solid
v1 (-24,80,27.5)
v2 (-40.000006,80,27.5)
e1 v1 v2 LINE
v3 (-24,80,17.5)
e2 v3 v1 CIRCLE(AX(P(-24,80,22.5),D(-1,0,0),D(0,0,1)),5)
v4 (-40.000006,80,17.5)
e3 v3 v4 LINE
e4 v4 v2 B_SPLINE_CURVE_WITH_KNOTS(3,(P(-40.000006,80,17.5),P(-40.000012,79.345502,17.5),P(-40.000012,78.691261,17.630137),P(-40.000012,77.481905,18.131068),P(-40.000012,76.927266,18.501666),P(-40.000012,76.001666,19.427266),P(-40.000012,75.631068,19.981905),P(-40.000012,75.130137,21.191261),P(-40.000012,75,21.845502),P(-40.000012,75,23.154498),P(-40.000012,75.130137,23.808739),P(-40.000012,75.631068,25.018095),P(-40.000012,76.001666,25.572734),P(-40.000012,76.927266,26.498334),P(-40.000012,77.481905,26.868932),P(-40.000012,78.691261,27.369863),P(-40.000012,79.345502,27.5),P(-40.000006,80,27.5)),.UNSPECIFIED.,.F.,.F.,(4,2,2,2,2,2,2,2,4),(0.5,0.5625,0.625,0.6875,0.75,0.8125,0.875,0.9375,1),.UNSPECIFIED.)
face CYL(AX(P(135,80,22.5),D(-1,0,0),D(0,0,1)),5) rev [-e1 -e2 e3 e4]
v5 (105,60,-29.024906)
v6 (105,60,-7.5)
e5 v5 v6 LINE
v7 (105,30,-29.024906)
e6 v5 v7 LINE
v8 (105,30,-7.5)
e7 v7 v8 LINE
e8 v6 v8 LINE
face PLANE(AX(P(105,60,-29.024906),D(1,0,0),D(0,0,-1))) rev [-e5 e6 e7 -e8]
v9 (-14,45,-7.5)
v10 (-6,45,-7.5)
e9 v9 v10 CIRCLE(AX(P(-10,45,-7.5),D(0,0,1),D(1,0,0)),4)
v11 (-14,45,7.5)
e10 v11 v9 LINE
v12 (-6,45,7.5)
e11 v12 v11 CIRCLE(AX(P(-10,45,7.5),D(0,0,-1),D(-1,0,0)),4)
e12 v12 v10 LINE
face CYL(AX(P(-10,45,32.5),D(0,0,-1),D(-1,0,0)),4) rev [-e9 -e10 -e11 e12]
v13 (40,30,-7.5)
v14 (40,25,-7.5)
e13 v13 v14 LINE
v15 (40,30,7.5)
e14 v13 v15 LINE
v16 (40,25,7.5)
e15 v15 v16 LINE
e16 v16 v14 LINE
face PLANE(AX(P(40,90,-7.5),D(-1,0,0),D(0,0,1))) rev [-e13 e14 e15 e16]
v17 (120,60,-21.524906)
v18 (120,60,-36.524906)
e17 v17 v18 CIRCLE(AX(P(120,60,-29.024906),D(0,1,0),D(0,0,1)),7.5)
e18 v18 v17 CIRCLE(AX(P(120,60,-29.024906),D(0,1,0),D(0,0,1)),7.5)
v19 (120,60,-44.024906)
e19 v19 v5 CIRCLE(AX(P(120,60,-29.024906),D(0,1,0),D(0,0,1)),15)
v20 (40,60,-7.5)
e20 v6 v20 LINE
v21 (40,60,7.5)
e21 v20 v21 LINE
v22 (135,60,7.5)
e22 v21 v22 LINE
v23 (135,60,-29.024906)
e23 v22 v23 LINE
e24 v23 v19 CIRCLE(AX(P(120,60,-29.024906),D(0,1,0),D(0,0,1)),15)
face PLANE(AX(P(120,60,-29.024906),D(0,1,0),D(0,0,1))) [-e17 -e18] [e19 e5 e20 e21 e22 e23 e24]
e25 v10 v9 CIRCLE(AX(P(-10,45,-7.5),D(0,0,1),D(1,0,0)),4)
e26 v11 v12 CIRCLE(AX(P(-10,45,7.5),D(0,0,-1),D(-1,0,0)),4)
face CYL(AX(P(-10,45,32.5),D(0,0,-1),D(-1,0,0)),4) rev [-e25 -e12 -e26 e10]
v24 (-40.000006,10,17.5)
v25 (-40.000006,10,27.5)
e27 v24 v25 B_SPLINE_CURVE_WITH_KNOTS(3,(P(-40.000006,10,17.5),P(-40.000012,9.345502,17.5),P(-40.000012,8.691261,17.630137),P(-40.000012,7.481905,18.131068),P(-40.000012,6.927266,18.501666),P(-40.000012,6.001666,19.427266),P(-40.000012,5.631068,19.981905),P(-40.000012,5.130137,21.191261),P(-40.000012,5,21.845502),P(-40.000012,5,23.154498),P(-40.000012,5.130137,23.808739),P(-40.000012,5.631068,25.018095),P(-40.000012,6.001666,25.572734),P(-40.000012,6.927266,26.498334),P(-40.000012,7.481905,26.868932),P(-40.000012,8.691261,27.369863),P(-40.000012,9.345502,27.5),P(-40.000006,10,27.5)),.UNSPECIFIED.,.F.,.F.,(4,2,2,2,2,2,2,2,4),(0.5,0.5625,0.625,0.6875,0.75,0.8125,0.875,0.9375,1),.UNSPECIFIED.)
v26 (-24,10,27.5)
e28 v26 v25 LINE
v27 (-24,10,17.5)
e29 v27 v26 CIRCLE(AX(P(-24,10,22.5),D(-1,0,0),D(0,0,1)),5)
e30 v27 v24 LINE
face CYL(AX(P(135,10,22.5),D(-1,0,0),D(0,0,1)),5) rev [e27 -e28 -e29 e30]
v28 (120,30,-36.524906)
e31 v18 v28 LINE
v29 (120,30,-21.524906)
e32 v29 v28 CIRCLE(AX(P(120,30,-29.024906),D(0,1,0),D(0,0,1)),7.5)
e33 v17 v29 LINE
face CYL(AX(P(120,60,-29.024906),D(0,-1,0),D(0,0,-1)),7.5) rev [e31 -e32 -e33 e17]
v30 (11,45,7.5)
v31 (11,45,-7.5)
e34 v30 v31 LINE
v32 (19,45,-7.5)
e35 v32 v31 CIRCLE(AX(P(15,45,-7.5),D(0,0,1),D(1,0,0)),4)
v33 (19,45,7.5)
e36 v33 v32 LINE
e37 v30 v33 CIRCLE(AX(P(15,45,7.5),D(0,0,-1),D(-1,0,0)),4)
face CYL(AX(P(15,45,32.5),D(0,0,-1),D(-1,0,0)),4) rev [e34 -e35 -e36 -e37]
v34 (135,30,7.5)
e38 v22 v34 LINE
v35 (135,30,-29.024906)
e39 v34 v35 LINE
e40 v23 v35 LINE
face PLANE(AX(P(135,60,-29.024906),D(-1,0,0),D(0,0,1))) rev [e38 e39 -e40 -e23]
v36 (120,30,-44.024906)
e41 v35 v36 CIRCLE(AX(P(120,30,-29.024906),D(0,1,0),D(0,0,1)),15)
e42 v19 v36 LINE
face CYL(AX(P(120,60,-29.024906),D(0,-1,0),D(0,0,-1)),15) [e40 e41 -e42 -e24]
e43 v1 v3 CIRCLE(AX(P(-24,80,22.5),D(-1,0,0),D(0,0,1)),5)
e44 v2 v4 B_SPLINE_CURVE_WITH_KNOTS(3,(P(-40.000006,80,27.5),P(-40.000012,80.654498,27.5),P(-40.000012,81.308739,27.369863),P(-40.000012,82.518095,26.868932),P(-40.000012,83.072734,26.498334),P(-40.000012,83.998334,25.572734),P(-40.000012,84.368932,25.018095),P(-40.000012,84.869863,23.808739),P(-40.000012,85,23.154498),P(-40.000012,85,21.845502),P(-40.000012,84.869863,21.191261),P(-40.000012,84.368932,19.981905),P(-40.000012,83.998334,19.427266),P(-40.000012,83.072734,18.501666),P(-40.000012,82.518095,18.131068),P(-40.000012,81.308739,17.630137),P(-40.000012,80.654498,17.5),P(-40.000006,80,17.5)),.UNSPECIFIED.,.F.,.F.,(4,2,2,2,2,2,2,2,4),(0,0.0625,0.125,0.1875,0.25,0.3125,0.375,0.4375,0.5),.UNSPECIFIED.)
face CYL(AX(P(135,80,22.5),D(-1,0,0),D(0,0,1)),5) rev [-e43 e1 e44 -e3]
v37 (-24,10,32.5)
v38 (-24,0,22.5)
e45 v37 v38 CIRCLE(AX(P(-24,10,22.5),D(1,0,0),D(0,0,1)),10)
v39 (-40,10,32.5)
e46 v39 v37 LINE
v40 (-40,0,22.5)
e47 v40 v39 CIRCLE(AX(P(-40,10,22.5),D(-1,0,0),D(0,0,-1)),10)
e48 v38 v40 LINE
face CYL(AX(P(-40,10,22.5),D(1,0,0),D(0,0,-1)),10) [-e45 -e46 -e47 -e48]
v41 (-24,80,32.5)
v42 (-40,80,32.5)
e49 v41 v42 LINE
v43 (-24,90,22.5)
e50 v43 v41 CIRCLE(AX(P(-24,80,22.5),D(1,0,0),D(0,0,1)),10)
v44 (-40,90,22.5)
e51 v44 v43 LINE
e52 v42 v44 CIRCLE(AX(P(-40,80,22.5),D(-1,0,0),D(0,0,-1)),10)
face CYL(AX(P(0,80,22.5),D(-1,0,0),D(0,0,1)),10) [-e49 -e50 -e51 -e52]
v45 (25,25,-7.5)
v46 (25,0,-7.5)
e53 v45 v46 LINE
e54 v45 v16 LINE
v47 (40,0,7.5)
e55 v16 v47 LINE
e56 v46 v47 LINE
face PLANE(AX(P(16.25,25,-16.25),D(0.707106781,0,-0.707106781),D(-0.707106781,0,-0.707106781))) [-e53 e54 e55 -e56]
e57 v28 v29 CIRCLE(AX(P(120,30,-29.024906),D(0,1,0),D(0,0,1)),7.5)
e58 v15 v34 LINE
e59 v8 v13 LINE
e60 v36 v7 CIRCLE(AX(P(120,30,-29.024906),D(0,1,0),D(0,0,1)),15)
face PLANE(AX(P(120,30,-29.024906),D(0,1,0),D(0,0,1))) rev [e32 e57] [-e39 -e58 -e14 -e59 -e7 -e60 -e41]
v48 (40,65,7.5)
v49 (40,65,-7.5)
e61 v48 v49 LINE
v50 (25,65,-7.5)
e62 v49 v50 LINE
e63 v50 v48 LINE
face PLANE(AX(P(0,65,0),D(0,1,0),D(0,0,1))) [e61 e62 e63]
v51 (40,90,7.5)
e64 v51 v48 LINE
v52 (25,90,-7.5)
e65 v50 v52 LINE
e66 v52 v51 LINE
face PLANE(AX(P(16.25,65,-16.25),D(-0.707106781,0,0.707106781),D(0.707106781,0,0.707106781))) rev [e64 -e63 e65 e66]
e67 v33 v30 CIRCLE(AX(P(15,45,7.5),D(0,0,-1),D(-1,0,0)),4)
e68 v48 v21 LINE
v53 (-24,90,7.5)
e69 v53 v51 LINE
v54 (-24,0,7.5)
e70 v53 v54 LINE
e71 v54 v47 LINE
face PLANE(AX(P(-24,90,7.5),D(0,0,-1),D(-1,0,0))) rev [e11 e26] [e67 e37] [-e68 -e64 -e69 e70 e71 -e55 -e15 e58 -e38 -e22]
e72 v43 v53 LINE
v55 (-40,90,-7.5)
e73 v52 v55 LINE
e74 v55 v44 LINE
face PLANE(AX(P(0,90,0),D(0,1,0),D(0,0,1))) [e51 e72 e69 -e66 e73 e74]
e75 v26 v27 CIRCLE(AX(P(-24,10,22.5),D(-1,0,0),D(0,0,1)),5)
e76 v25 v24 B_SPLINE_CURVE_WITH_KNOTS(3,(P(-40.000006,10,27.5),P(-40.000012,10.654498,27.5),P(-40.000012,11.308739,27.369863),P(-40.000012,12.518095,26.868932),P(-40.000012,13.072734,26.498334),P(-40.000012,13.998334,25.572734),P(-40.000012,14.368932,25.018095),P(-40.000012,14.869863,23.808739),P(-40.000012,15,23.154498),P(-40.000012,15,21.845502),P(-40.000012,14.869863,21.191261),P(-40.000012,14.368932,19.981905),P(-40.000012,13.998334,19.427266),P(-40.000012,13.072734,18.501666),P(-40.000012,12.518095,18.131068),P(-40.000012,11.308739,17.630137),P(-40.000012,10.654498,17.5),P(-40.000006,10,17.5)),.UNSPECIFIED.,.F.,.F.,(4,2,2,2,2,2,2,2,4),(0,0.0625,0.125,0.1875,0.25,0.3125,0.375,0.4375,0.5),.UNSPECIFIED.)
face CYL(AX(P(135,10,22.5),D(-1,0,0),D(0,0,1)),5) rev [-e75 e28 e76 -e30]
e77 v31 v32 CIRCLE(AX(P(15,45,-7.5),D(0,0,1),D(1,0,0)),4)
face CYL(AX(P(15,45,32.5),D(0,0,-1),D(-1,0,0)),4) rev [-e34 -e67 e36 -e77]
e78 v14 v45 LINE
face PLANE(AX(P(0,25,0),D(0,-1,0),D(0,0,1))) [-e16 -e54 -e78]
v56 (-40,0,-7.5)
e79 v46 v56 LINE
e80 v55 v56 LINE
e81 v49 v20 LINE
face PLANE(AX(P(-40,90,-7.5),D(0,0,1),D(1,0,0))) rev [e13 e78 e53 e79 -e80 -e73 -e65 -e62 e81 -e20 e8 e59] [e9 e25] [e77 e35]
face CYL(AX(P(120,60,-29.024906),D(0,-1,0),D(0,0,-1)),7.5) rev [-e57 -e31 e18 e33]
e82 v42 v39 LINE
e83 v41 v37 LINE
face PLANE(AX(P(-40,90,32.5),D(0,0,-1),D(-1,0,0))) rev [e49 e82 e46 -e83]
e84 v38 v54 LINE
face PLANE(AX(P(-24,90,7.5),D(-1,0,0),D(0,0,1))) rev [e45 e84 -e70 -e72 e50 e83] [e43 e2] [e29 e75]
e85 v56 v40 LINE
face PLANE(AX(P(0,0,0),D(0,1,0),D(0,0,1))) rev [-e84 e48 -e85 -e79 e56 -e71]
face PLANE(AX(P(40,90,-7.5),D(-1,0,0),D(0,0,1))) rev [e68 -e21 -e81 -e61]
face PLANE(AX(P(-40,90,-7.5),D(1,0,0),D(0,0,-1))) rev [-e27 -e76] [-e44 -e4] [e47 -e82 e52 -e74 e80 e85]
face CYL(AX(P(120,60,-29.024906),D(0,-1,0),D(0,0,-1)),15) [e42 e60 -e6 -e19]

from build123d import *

# Parameters (mm, degrees)
BRACKET_BODY_DEPTH         = 90
ANGLED_CUT_DEPTH           = 25
ARM_BOSS_SKETCH_R          = 7.5
ARM_BOSS_DEPTH             = 15
CORNER_FILLETS_R10_R       = 10
CORNER_HOLES_10_DEPTH      = 202.651164925
CORNER_HOLES_10_DEPTH_BACK = 202.651164925
CORNER_HOLES_SKETCH_R      = 5
FACE_HOLES_2X_8_DEPTH      = 168.107749671
FACE_HOLES_2X_8_DEPTH_BACK = 168.107749671
FACE_HOLES_SKETCH_R        = 4


with BuildPart() as part:
    # Bracket Profile Sketch → Bracket Body (new body)
    with BuildSketch(Plane(origin=(0, 0, 0), x_dir=(1, 0, 0), z_dir=(0, 1, 0))):
        Polygon((-24, -7.5), (-24, -32.5), (-40, -32.5), (-40, 7.5), (-24, 7.5), (40, 7.5), (40, -7.5), align=None)
    extrude(amount=BRACKET_BODY_DEPTH)

    # Angled Cut Sketch → Angled Cut (cut)
    with BuildSketch(Plane(origin=(0, 90, 0), x_dir=(1, 0, 0), z_dir=(0, 1, 0))):
        Polygon((40, 7.5), (25, 7.5), (40, -7.5), align=None)
    angled_cut = extrude(amount=-ANGLED_CUT_DEPTH, mode=Mode.SUBTRACT)

    # Angled Cut Mirror: Angled Cut across plane
    add(angled_cut.mirror(Plane.ZX.offset(45)), mode=Mode.SUBTRACT)

    # Arm Boss Sketch → Arm Boss (add, symmetric)
    with BuildSketch(Plane(origin=(0, 45, 0), x_dir=(1, 0, 0), z_dir=(0, 1, 0))):
        with BuildLine():
            Line((40, -7.5), (135, -7.5))
            Line((135, -7.5), (135, 29.024905628))
            ThreePointArc((135, 29.024905628), (120, 44.024905628), (105, 29.024905628))
            Line((105, 29.024905628), (105, 7.5))
            Line((105, 7.5), (40, 7.5))
            Line((40, 7.5), (40, -7.5))
        make_face()
        with Locations(Location((120, 29.024905628, 0), (0, 0, 270))):
            Circle(ARM_BOSS_SKETCH_R, mode=Mode.SUBTRACT)
    extrude(amount=ARM_BOSS_DEPTH, both=True)

    # Corner Fillets R10
    corner_fillets_r10_edges = [part.edges().sort_by_distance(p)[0] for p in [
        (-32, 90, 32.5),
        (-32, 0, 32.5),
    ]]
    fillet(corner_fillets_r10_edges, radius=CORNER_FILLETS_R10_R)

    # Corner Holes Sketch → Corner Holes Ø10 (cut, two sides: drawn at the far end of the back side and taken through both)
    with BuildSketch(Plane.ZY.offset(40).offset(-CORNER_HOLES_10_DEPTH_BACK)):
        with Locations((22.5, 80)):
            Circle(CORNER_HOLES_SKETCH_R)
        with Locations((22.5, 10)):
            Circle(CORNER_HOLES_SKETCH_R)
    extrude(amount=CORNER_HOLES_10_DEPTH + CORNER_HOLES_10_DEPTH_BACK, mode=Mode.SUBTRACT)

    # Face Holes Sketch → Face Holes 2xØ8 (cut, two sides: drawn at the far end of the back side and taken through both)
    with BuildSketch(Plane(origin=(0, 0, -7.5), x_dir=(-1, 0, 0), z_dir=(0, 0, -1)).offset(-FACE_HOLES_2X_8_DEPTH_BACK)):
        with Locations((10, 45)):
            Circle(FACE_HOLES_SKETCH_R)
        with Locations((-15, 45)):
            Circle(FACE_HOLES_SKETCH_R)
    extrude(amount=FACE_HOLES_2X_8_DEPTH + FACE_HOLES_2X_8_DEPTH_BACK, mode=Mode.SUBTRACT)


solid = part.part
